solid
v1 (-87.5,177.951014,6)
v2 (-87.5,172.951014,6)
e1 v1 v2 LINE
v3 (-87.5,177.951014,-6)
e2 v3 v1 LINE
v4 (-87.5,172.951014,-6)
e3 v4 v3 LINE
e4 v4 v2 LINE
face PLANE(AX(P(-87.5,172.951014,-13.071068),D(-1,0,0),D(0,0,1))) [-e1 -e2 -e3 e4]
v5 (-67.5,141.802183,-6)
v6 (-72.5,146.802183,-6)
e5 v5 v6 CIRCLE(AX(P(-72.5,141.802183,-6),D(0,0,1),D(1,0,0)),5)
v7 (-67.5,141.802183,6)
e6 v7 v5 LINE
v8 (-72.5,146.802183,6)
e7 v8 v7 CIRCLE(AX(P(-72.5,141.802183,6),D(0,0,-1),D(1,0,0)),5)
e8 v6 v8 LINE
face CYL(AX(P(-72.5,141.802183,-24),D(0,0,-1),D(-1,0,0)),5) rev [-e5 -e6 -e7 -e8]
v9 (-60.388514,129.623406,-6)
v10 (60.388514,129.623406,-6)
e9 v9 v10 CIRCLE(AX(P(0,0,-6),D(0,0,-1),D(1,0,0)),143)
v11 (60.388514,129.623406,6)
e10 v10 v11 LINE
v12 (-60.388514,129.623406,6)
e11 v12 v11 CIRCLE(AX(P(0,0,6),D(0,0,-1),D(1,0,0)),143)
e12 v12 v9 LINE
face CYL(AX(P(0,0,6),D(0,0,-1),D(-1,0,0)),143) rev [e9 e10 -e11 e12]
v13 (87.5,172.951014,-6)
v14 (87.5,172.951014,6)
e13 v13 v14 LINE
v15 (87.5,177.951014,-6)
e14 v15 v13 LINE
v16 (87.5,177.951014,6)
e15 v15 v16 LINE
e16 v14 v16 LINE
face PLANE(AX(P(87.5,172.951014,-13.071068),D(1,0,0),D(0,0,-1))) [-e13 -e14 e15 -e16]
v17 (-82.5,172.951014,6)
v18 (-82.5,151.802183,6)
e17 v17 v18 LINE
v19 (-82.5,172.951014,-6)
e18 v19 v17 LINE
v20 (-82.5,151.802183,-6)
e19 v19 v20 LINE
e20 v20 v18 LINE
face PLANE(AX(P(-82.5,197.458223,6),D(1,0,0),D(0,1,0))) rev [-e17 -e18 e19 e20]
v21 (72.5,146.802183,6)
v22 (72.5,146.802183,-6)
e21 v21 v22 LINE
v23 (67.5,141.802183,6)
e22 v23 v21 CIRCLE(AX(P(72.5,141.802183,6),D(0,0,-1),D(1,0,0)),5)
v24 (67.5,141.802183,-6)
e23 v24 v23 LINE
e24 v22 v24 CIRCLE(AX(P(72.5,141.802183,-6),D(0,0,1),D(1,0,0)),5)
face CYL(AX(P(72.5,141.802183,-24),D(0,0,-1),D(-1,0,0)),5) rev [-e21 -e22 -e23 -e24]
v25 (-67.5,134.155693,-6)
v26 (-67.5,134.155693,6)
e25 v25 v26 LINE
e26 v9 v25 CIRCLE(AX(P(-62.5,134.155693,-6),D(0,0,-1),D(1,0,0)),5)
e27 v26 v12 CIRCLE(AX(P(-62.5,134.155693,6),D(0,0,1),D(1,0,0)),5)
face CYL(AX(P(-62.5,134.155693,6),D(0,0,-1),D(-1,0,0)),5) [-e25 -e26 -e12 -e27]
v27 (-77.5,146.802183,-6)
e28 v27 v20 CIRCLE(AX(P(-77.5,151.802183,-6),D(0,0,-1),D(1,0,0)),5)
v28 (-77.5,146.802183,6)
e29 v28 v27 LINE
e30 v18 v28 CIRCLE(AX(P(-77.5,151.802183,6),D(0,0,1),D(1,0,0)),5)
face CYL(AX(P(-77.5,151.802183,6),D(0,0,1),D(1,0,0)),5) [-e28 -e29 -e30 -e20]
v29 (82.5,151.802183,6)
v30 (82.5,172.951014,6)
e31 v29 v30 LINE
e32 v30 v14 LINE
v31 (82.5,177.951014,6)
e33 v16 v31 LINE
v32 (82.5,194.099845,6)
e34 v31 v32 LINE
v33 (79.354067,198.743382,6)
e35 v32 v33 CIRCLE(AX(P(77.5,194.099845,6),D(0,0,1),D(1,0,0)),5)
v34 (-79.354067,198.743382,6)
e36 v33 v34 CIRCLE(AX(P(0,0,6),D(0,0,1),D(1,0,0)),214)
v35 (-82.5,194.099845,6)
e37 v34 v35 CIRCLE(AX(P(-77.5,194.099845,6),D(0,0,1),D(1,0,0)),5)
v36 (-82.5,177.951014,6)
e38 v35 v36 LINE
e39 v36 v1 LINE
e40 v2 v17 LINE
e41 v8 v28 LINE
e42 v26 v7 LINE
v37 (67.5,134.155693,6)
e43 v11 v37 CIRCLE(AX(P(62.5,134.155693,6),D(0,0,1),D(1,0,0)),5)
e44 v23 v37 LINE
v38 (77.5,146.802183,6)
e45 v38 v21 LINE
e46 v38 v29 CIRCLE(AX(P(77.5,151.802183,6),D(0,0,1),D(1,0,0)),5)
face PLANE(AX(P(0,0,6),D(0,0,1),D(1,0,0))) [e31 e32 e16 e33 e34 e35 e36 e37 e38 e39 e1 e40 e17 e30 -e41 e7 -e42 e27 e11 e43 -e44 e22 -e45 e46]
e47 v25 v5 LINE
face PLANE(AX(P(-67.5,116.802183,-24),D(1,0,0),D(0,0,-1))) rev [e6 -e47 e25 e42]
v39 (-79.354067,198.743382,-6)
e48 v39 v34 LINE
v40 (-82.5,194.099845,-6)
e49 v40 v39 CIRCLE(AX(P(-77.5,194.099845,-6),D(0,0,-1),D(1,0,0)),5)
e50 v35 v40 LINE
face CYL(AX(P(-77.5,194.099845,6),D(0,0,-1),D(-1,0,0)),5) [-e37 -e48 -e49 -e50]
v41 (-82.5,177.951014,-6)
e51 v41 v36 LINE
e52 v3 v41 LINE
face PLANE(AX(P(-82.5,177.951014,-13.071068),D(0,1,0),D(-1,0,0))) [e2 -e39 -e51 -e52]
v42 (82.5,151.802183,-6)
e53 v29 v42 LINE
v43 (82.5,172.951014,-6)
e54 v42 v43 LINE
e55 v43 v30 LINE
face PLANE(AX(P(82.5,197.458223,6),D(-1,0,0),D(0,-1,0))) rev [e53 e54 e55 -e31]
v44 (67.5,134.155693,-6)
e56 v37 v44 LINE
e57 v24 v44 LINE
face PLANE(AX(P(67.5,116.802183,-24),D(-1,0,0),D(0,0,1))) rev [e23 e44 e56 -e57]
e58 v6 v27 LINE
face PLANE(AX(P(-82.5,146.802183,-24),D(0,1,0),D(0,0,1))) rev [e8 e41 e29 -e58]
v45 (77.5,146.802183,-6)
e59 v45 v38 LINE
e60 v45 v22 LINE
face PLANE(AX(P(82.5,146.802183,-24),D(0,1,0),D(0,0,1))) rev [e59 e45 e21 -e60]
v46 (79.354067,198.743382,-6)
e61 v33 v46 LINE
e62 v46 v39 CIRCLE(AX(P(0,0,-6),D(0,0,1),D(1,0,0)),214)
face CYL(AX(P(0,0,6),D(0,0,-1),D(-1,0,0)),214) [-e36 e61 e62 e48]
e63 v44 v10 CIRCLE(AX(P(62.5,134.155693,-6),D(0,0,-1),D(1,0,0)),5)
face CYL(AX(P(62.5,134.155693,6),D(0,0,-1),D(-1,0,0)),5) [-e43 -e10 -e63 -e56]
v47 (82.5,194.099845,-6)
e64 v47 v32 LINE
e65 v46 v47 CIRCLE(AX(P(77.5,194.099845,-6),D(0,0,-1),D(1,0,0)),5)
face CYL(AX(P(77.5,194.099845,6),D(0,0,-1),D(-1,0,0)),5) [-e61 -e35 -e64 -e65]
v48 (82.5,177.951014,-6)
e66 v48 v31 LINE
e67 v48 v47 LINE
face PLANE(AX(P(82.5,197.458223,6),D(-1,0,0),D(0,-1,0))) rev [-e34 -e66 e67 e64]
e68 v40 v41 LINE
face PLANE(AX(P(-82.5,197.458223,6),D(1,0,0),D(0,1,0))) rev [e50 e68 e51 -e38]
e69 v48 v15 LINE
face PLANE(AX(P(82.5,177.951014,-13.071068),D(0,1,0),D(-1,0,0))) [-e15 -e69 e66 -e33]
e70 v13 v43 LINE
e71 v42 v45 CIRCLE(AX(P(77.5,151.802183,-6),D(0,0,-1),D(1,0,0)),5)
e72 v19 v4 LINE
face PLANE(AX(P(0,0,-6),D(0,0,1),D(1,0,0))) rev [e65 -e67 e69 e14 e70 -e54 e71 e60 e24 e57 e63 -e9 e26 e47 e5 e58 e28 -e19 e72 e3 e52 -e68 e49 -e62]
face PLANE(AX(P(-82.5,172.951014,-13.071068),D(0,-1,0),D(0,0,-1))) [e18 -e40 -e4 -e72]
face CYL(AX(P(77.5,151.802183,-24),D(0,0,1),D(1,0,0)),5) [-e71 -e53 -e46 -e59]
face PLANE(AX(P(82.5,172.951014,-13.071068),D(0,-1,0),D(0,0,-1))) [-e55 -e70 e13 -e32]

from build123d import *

# Parameters (mm, degrees)
BOSS_EXTRUDE1_DEPTH = 6
SKETCH2_W           = 15
SKETCH2_H           = 30
CUT_EXTRUDE1_DEPTH  = 30
FILLET2_R           = 5
SKETCH3_W           = 5
SKETCH3_H           = 5
BOSS_EXTRUDE2_DEPTH = 12


with BuildPart() as part:
    # Sketch1 → Boss-Extrude1 (new, symmetric)
    with BuildSketch(Plane.XY):
        with BuildLine():
            Line((-82.5, 197.45822343), (-82.5, 116.802183199))
            ThreePointArc((-82.5, 116.802183199), (0, 143), (82.5, 116.802183199))
            Line((82.5, 116.802183199), (82.5, 197.45822343))
            ThreePointArc((82.5, 197.45822343), (0, 214), (-82.5, 197.45822343))
        make_face()
    extrude(amount=BOSS_EXTRUDE1_DEPTH, both=True)

    # Sketch2 → Cut-Extrude1 (cut)
    with BuildSketch(Plane.XY.offset(6)):
        with Locations((-75, 131.802183199)):
            Rectangle(SKETCH2_W, SKETCH2_H)
        with Locations((75, 131.802183199)):
            Rectangle(SKETCH2_W, SKETCH2_H)
    extrude(amount=-CUT_EXTRUDE1_DEPTH, mode=Mode.SUBTRACT)

    # Fillet2
    fillet2_edges = [part.edges().sort_by_distance(p)[0] for p in [
        (-82.5, 146.802183199, 0),
        (-67.5, 126.066450731, 0),
        (-67.5, 146.802183199, 0),
        (82.5, 146.802183199, 0),
        (67.5, 126.066450731, 0),
        (67.5, 146.802183199, 0),
        (-82.5, 197.45822343, 0),
        (82.5, 197.45822343, 0),
    ]]
    fillet(fillet2_edges, radius=FILLET2_R)

    # Sketch3 → Boss-Extrude2 (add)
    with BuildSketch(Plane.XY.offset(6)):
        with Locations((85, 175.45101432)):
            Rectangle(SKETCH3_W, SKETCH3_H)
        with Locations((-85, 175.45101432)):
            Rectangle(SKETCH3_W, SKETCH3_H)
    extrude(amount=-BOSS_EXTRUDE2_DEPTH)


solid = part.part
